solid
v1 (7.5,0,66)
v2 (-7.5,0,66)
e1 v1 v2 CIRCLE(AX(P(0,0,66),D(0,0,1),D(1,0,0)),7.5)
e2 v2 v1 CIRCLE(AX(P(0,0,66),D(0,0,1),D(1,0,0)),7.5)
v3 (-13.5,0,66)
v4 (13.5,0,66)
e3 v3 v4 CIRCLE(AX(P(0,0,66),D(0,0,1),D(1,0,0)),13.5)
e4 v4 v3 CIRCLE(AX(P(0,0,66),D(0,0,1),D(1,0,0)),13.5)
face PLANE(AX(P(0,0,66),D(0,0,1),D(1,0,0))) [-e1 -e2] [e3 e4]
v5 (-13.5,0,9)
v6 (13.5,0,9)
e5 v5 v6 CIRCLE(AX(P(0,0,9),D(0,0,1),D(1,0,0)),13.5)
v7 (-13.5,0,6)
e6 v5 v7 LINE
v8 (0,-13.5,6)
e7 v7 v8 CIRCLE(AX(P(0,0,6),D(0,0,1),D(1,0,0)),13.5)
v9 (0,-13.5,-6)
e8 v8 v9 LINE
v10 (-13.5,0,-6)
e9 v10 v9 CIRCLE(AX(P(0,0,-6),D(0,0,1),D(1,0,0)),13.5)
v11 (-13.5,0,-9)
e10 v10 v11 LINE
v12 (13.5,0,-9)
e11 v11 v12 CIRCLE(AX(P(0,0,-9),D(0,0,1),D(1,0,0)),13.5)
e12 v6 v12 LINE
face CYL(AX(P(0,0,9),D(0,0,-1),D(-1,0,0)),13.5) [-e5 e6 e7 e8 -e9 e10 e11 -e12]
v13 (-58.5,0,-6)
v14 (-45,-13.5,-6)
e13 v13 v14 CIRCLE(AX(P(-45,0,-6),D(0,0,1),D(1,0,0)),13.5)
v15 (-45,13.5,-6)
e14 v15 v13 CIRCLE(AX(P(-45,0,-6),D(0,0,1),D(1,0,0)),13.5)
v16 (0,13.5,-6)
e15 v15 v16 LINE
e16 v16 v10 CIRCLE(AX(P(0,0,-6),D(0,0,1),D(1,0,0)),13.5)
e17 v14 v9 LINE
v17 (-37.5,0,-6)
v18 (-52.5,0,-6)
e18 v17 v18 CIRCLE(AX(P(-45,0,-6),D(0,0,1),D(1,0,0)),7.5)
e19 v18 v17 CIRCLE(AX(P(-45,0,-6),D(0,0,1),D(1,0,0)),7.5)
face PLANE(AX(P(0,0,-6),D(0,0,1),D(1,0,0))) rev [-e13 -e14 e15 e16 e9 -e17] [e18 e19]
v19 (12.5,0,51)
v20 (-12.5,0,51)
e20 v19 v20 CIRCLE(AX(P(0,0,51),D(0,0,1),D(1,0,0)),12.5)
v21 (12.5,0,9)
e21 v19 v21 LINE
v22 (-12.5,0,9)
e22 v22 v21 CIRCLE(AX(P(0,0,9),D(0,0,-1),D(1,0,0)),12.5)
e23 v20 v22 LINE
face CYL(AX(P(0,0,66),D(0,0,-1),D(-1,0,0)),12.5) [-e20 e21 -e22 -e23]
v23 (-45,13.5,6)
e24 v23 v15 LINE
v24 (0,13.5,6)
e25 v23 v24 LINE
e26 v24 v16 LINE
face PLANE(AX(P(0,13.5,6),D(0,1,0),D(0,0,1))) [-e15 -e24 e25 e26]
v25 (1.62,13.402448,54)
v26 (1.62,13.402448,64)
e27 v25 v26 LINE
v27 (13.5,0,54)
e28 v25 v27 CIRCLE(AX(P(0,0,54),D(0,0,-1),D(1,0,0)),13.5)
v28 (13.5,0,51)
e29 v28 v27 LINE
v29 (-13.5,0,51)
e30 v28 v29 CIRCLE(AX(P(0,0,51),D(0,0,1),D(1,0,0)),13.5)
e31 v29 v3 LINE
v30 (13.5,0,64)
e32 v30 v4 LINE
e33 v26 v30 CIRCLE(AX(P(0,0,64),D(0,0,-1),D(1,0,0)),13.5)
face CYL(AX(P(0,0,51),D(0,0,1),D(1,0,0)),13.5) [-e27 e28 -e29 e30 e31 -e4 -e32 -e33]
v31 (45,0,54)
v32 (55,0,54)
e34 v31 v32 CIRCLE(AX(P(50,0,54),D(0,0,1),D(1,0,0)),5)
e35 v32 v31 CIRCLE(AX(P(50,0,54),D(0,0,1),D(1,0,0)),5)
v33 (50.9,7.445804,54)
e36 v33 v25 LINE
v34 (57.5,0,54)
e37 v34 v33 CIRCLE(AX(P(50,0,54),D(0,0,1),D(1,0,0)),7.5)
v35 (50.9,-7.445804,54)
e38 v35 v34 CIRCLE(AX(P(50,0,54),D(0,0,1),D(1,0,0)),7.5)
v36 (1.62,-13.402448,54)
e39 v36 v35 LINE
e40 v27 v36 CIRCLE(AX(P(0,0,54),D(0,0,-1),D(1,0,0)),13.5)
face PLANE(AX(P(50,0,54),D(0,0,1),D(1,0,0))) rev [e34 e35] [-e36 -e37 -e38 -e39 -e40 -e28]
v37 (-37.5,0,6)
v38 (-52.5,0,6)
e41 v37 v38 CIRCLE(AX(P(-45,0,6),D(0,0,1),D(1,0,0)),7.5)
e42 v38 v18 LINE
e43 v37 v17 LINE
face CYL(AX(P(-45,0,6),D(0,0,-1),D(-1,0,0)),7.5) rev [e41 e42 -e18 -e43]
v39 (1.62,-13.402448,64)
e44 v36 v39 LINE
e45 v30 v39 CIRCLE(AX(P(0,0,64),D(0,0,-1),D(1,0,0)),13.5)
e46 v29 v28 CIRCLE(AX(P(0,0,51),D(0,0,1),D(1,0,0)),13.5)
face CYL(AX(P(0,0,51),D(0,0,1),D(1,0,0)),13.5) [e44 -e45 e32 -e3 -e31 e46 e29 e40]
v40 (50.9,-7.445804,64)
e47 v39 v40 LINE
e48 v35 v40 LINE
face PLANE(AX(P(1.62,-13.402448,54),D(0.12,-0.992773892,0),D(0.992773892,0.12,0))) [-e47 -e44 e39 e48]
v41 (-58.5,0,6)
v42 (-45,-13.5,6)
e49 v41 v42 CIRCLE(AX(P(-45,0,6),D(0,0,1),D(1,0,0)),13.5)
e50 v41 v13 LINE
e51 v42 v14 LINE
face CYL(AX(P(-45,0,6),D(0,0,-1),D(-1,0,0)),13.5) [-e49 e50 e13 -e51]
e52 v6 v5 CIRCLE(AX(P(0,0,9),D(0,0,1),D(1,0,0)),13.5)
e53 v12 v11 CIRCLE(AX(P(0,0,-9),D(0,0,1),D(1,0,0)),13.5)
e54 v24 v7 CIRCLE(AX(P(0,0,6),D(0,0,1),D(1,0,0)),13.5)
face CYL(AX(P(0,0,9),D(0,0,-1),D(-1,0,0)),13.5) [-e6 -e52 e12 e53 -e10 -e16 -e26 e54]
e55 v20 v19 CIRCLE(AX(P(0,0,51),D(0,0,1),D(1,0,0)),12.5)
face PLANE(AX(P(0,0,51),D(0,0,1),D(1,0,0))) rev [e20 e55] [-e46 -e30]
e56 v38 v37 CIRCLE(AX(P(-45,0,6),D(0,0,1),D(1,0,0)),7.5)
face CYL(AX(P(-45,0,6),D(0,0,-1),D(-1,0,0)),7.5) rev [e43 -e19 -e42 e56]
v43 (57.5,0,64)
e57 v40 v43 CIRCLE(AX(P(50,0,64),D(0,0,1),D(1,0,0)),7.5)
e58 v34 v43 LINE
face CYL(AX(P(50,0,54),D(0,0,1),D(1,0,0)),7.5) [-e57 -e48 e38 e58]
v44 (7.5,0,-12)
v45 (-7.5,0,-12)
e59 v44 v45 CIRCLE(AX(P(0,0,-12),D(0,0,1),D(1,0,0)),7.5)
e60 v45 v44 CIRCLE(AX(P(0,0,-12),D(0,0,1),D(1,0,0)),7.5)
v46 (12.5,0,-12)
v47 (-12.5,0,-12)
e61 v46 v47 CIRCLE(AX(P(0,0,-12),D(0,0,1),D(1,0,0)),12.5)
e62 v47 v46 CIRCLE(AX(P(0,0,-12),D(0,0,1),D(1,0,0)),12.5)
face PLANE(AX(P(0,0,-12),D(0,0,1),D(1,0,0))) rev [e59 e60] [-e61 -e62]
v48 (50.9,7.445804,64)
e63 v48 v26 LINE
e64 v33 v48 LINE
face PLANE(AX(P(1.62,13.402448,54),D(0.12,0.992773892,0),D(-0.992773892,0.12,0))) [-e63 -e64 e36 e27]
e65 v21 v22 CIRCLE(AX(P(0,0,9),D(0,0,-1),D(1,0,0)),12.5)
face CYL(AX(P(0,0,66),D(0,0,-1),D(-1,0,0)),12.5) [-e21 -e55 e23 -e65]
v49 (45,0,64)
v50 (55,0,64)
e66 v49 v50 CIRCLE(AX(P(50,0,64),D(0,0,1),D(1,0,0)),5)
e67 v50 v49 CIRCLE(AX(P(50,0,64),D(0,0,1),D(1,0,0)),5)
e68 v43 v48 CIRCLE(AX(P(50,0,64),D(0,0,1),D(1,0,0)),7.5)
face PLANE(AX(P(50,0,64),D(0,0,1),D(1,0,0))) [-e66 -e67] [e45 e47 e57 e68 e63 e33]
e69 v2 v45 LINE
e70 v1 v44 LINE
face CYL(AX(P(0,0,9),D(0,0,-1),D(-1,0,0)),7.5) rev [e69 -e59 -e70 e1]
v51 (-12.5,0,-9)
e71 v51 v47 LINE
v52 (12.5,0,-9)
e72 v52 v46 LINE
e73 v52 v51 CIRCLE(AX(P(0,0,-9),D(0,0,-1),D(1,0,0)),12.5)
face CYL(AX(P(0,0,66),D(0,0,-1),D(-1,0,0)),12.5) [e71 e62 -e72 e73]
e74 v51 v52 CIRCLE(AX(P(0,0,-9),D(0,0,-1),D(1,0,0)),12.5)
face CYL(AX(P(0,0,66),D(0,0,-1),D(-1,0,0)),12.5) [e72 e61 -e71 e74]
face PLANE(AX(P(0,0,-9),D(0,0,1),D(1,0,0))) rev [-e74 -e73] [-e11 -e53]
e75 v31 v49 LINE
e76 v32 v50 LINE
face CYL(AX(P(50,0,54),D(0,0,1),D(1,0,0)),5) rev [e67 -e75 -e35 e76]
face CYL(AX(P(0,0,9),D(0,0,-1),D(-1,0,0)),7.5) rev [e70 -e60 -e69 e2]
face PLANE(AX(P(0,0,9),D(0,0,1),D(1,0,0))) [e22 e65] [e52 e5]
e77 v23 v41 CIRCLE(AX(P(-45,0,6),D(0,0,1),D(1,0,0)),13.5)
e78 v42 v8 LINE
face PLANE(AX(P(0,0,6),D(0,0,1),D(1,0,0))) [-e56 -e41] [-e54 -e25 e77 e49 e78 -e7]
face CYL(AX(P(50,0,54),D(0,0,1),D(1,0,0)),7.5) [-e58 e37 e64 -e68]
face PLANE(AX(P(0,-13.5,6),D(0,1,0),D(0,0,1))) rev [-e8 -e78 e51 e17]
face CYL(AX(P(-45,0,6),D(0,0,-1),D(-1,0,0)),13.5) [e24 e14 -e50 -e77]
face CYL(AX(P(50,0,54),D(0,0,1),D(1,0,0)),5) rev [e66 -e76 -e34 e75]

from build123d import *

# Parameters (mm, degrees)
LOWER_ARM_PROFILE_SKETCH_R   = 13.5
LOWER_ARM_PROFILE_SKETCH_R_2 = 7.5
LOWER_CRANK_ARM_DEPTH        = 9
SKETCH1_3_R                  = 7.5
LOWER_ARM_HUB_BOSS_DEPTH     = 6
SHAFT_25_DEPTH               = 75
SHAFT_25_DEPTH_BACK          = 3
SHAFT_25_START               = -9
SHAFT_25_SKETCH_R            = 12.5
SHAFT_25_SKETCH_R_2          = 7.5
SHAFT_COLLAR_SKETCH_R        = 13.5
SHAFT_COLLAR_SKETCH_R_2      = 7.5
SHAFT_COLLAR_DEPTH           = 15
UPPER_START                  = -2
UPPER_ARM_PROFILE_SKETCH_R   = 5
UPPER_CRANK_ARM_DEPTH        = 10


with BuildPart() as part:
    # Lower Arm Profile Sketch → Lower Crank Arm (new, symmetric)
    with BuildSketch(Plane.XY):
        Circle(LOWER_ARM_PROFILE_SKETCH_R)
        Circle(LOWER_ARM_PROFILE_SKETCH_R_2, mode=Mode.SUBTRACT)
    extrude(amount=LOWER_CRANK_ARM_DEPTH, both=True)



with BuildPart() as body_2:
    # Sketch1_3 → Lower Arm Hub Boss (new, symmetric)
    with BuildSketch(Plane.XY):
        with BuildLine():
            ThreePointArc((-45, 13.5), (-58.5, 0), (-45, -13.5))
            Line((-45, -13.5), (0, -13.5))
            ThreePointArc((0, -13.5), (-13.5, 0), (0, 13.5))
            Line((0, 13.5), (-45, 13.5))
        make_face()
        with Locations((-45, 0)):
            Circle(SKETCH1_3_R, mode=Mode.SUBTRACT)
    extrude(amount=LOWER_ARM_HUB_BOSS_DEPTH, both=True)


with BuildPart() as part_1:
    add(part.part)

    add(body_2.part)  # Shaft _25 merges body 2
    # Shaft _25 Sketch → Shaft _25 (add, two sides: drawn at the far end of the back side and taken through both)
    with BuildSketch(Plane.XY.offset(SHAFT_25_START - SHAFT_25_DEPTH_BACK)):
        Circle(SHAFT_25_SKETCH_R)
        Circle(SHAFT_25_SKETCH_R_2, mode=Mode.SUBTRACT)
    extrude(amount=SHAFT_25_DEPTH + SHAFT_25_DEPTH_BACK)

    # Shaft Collar Sketch → Shaft Collar (add)
    with BuildSketch(Plane.XY.offset(66)):
        Circle(SHAFT_COLLAR_SKETCH_R)
        Circle(SHAFT_COLLAR_SKETCH_R_2, mode=Mode.SUBTRACT)
    extrude(amount=-SHAFT_COLLAR_DEPTH)

    # Upper Arm Profile Sketch → Upper Crank Arm (add)
    with BuildSketch(Plane.XY.offset(66).offset(UPPER_START)):
        with BuildLine():
            Line((1.62, 13.402447538), (50.9, 7.445804188))
            ThreePointArc((50.9, 7.445804188), (57.5, 0), (50.9, -7.445804188))
            Line((50.9, -7.445804188), (1.62, -13.402447538))
            ThreePointArc((1.62, -13.402447538), (13.5, 0), (1.62, 13.402447538))
        make_face()
        with Locations((50, 0)):
            Circle(UPPER_ARM_PROFILE_SKETCH_R, mode=Mode.SUBTRACT)
    extrude(amount=-UPPER_CRANK_ARM_DEPTH)


solid = part_1.part
